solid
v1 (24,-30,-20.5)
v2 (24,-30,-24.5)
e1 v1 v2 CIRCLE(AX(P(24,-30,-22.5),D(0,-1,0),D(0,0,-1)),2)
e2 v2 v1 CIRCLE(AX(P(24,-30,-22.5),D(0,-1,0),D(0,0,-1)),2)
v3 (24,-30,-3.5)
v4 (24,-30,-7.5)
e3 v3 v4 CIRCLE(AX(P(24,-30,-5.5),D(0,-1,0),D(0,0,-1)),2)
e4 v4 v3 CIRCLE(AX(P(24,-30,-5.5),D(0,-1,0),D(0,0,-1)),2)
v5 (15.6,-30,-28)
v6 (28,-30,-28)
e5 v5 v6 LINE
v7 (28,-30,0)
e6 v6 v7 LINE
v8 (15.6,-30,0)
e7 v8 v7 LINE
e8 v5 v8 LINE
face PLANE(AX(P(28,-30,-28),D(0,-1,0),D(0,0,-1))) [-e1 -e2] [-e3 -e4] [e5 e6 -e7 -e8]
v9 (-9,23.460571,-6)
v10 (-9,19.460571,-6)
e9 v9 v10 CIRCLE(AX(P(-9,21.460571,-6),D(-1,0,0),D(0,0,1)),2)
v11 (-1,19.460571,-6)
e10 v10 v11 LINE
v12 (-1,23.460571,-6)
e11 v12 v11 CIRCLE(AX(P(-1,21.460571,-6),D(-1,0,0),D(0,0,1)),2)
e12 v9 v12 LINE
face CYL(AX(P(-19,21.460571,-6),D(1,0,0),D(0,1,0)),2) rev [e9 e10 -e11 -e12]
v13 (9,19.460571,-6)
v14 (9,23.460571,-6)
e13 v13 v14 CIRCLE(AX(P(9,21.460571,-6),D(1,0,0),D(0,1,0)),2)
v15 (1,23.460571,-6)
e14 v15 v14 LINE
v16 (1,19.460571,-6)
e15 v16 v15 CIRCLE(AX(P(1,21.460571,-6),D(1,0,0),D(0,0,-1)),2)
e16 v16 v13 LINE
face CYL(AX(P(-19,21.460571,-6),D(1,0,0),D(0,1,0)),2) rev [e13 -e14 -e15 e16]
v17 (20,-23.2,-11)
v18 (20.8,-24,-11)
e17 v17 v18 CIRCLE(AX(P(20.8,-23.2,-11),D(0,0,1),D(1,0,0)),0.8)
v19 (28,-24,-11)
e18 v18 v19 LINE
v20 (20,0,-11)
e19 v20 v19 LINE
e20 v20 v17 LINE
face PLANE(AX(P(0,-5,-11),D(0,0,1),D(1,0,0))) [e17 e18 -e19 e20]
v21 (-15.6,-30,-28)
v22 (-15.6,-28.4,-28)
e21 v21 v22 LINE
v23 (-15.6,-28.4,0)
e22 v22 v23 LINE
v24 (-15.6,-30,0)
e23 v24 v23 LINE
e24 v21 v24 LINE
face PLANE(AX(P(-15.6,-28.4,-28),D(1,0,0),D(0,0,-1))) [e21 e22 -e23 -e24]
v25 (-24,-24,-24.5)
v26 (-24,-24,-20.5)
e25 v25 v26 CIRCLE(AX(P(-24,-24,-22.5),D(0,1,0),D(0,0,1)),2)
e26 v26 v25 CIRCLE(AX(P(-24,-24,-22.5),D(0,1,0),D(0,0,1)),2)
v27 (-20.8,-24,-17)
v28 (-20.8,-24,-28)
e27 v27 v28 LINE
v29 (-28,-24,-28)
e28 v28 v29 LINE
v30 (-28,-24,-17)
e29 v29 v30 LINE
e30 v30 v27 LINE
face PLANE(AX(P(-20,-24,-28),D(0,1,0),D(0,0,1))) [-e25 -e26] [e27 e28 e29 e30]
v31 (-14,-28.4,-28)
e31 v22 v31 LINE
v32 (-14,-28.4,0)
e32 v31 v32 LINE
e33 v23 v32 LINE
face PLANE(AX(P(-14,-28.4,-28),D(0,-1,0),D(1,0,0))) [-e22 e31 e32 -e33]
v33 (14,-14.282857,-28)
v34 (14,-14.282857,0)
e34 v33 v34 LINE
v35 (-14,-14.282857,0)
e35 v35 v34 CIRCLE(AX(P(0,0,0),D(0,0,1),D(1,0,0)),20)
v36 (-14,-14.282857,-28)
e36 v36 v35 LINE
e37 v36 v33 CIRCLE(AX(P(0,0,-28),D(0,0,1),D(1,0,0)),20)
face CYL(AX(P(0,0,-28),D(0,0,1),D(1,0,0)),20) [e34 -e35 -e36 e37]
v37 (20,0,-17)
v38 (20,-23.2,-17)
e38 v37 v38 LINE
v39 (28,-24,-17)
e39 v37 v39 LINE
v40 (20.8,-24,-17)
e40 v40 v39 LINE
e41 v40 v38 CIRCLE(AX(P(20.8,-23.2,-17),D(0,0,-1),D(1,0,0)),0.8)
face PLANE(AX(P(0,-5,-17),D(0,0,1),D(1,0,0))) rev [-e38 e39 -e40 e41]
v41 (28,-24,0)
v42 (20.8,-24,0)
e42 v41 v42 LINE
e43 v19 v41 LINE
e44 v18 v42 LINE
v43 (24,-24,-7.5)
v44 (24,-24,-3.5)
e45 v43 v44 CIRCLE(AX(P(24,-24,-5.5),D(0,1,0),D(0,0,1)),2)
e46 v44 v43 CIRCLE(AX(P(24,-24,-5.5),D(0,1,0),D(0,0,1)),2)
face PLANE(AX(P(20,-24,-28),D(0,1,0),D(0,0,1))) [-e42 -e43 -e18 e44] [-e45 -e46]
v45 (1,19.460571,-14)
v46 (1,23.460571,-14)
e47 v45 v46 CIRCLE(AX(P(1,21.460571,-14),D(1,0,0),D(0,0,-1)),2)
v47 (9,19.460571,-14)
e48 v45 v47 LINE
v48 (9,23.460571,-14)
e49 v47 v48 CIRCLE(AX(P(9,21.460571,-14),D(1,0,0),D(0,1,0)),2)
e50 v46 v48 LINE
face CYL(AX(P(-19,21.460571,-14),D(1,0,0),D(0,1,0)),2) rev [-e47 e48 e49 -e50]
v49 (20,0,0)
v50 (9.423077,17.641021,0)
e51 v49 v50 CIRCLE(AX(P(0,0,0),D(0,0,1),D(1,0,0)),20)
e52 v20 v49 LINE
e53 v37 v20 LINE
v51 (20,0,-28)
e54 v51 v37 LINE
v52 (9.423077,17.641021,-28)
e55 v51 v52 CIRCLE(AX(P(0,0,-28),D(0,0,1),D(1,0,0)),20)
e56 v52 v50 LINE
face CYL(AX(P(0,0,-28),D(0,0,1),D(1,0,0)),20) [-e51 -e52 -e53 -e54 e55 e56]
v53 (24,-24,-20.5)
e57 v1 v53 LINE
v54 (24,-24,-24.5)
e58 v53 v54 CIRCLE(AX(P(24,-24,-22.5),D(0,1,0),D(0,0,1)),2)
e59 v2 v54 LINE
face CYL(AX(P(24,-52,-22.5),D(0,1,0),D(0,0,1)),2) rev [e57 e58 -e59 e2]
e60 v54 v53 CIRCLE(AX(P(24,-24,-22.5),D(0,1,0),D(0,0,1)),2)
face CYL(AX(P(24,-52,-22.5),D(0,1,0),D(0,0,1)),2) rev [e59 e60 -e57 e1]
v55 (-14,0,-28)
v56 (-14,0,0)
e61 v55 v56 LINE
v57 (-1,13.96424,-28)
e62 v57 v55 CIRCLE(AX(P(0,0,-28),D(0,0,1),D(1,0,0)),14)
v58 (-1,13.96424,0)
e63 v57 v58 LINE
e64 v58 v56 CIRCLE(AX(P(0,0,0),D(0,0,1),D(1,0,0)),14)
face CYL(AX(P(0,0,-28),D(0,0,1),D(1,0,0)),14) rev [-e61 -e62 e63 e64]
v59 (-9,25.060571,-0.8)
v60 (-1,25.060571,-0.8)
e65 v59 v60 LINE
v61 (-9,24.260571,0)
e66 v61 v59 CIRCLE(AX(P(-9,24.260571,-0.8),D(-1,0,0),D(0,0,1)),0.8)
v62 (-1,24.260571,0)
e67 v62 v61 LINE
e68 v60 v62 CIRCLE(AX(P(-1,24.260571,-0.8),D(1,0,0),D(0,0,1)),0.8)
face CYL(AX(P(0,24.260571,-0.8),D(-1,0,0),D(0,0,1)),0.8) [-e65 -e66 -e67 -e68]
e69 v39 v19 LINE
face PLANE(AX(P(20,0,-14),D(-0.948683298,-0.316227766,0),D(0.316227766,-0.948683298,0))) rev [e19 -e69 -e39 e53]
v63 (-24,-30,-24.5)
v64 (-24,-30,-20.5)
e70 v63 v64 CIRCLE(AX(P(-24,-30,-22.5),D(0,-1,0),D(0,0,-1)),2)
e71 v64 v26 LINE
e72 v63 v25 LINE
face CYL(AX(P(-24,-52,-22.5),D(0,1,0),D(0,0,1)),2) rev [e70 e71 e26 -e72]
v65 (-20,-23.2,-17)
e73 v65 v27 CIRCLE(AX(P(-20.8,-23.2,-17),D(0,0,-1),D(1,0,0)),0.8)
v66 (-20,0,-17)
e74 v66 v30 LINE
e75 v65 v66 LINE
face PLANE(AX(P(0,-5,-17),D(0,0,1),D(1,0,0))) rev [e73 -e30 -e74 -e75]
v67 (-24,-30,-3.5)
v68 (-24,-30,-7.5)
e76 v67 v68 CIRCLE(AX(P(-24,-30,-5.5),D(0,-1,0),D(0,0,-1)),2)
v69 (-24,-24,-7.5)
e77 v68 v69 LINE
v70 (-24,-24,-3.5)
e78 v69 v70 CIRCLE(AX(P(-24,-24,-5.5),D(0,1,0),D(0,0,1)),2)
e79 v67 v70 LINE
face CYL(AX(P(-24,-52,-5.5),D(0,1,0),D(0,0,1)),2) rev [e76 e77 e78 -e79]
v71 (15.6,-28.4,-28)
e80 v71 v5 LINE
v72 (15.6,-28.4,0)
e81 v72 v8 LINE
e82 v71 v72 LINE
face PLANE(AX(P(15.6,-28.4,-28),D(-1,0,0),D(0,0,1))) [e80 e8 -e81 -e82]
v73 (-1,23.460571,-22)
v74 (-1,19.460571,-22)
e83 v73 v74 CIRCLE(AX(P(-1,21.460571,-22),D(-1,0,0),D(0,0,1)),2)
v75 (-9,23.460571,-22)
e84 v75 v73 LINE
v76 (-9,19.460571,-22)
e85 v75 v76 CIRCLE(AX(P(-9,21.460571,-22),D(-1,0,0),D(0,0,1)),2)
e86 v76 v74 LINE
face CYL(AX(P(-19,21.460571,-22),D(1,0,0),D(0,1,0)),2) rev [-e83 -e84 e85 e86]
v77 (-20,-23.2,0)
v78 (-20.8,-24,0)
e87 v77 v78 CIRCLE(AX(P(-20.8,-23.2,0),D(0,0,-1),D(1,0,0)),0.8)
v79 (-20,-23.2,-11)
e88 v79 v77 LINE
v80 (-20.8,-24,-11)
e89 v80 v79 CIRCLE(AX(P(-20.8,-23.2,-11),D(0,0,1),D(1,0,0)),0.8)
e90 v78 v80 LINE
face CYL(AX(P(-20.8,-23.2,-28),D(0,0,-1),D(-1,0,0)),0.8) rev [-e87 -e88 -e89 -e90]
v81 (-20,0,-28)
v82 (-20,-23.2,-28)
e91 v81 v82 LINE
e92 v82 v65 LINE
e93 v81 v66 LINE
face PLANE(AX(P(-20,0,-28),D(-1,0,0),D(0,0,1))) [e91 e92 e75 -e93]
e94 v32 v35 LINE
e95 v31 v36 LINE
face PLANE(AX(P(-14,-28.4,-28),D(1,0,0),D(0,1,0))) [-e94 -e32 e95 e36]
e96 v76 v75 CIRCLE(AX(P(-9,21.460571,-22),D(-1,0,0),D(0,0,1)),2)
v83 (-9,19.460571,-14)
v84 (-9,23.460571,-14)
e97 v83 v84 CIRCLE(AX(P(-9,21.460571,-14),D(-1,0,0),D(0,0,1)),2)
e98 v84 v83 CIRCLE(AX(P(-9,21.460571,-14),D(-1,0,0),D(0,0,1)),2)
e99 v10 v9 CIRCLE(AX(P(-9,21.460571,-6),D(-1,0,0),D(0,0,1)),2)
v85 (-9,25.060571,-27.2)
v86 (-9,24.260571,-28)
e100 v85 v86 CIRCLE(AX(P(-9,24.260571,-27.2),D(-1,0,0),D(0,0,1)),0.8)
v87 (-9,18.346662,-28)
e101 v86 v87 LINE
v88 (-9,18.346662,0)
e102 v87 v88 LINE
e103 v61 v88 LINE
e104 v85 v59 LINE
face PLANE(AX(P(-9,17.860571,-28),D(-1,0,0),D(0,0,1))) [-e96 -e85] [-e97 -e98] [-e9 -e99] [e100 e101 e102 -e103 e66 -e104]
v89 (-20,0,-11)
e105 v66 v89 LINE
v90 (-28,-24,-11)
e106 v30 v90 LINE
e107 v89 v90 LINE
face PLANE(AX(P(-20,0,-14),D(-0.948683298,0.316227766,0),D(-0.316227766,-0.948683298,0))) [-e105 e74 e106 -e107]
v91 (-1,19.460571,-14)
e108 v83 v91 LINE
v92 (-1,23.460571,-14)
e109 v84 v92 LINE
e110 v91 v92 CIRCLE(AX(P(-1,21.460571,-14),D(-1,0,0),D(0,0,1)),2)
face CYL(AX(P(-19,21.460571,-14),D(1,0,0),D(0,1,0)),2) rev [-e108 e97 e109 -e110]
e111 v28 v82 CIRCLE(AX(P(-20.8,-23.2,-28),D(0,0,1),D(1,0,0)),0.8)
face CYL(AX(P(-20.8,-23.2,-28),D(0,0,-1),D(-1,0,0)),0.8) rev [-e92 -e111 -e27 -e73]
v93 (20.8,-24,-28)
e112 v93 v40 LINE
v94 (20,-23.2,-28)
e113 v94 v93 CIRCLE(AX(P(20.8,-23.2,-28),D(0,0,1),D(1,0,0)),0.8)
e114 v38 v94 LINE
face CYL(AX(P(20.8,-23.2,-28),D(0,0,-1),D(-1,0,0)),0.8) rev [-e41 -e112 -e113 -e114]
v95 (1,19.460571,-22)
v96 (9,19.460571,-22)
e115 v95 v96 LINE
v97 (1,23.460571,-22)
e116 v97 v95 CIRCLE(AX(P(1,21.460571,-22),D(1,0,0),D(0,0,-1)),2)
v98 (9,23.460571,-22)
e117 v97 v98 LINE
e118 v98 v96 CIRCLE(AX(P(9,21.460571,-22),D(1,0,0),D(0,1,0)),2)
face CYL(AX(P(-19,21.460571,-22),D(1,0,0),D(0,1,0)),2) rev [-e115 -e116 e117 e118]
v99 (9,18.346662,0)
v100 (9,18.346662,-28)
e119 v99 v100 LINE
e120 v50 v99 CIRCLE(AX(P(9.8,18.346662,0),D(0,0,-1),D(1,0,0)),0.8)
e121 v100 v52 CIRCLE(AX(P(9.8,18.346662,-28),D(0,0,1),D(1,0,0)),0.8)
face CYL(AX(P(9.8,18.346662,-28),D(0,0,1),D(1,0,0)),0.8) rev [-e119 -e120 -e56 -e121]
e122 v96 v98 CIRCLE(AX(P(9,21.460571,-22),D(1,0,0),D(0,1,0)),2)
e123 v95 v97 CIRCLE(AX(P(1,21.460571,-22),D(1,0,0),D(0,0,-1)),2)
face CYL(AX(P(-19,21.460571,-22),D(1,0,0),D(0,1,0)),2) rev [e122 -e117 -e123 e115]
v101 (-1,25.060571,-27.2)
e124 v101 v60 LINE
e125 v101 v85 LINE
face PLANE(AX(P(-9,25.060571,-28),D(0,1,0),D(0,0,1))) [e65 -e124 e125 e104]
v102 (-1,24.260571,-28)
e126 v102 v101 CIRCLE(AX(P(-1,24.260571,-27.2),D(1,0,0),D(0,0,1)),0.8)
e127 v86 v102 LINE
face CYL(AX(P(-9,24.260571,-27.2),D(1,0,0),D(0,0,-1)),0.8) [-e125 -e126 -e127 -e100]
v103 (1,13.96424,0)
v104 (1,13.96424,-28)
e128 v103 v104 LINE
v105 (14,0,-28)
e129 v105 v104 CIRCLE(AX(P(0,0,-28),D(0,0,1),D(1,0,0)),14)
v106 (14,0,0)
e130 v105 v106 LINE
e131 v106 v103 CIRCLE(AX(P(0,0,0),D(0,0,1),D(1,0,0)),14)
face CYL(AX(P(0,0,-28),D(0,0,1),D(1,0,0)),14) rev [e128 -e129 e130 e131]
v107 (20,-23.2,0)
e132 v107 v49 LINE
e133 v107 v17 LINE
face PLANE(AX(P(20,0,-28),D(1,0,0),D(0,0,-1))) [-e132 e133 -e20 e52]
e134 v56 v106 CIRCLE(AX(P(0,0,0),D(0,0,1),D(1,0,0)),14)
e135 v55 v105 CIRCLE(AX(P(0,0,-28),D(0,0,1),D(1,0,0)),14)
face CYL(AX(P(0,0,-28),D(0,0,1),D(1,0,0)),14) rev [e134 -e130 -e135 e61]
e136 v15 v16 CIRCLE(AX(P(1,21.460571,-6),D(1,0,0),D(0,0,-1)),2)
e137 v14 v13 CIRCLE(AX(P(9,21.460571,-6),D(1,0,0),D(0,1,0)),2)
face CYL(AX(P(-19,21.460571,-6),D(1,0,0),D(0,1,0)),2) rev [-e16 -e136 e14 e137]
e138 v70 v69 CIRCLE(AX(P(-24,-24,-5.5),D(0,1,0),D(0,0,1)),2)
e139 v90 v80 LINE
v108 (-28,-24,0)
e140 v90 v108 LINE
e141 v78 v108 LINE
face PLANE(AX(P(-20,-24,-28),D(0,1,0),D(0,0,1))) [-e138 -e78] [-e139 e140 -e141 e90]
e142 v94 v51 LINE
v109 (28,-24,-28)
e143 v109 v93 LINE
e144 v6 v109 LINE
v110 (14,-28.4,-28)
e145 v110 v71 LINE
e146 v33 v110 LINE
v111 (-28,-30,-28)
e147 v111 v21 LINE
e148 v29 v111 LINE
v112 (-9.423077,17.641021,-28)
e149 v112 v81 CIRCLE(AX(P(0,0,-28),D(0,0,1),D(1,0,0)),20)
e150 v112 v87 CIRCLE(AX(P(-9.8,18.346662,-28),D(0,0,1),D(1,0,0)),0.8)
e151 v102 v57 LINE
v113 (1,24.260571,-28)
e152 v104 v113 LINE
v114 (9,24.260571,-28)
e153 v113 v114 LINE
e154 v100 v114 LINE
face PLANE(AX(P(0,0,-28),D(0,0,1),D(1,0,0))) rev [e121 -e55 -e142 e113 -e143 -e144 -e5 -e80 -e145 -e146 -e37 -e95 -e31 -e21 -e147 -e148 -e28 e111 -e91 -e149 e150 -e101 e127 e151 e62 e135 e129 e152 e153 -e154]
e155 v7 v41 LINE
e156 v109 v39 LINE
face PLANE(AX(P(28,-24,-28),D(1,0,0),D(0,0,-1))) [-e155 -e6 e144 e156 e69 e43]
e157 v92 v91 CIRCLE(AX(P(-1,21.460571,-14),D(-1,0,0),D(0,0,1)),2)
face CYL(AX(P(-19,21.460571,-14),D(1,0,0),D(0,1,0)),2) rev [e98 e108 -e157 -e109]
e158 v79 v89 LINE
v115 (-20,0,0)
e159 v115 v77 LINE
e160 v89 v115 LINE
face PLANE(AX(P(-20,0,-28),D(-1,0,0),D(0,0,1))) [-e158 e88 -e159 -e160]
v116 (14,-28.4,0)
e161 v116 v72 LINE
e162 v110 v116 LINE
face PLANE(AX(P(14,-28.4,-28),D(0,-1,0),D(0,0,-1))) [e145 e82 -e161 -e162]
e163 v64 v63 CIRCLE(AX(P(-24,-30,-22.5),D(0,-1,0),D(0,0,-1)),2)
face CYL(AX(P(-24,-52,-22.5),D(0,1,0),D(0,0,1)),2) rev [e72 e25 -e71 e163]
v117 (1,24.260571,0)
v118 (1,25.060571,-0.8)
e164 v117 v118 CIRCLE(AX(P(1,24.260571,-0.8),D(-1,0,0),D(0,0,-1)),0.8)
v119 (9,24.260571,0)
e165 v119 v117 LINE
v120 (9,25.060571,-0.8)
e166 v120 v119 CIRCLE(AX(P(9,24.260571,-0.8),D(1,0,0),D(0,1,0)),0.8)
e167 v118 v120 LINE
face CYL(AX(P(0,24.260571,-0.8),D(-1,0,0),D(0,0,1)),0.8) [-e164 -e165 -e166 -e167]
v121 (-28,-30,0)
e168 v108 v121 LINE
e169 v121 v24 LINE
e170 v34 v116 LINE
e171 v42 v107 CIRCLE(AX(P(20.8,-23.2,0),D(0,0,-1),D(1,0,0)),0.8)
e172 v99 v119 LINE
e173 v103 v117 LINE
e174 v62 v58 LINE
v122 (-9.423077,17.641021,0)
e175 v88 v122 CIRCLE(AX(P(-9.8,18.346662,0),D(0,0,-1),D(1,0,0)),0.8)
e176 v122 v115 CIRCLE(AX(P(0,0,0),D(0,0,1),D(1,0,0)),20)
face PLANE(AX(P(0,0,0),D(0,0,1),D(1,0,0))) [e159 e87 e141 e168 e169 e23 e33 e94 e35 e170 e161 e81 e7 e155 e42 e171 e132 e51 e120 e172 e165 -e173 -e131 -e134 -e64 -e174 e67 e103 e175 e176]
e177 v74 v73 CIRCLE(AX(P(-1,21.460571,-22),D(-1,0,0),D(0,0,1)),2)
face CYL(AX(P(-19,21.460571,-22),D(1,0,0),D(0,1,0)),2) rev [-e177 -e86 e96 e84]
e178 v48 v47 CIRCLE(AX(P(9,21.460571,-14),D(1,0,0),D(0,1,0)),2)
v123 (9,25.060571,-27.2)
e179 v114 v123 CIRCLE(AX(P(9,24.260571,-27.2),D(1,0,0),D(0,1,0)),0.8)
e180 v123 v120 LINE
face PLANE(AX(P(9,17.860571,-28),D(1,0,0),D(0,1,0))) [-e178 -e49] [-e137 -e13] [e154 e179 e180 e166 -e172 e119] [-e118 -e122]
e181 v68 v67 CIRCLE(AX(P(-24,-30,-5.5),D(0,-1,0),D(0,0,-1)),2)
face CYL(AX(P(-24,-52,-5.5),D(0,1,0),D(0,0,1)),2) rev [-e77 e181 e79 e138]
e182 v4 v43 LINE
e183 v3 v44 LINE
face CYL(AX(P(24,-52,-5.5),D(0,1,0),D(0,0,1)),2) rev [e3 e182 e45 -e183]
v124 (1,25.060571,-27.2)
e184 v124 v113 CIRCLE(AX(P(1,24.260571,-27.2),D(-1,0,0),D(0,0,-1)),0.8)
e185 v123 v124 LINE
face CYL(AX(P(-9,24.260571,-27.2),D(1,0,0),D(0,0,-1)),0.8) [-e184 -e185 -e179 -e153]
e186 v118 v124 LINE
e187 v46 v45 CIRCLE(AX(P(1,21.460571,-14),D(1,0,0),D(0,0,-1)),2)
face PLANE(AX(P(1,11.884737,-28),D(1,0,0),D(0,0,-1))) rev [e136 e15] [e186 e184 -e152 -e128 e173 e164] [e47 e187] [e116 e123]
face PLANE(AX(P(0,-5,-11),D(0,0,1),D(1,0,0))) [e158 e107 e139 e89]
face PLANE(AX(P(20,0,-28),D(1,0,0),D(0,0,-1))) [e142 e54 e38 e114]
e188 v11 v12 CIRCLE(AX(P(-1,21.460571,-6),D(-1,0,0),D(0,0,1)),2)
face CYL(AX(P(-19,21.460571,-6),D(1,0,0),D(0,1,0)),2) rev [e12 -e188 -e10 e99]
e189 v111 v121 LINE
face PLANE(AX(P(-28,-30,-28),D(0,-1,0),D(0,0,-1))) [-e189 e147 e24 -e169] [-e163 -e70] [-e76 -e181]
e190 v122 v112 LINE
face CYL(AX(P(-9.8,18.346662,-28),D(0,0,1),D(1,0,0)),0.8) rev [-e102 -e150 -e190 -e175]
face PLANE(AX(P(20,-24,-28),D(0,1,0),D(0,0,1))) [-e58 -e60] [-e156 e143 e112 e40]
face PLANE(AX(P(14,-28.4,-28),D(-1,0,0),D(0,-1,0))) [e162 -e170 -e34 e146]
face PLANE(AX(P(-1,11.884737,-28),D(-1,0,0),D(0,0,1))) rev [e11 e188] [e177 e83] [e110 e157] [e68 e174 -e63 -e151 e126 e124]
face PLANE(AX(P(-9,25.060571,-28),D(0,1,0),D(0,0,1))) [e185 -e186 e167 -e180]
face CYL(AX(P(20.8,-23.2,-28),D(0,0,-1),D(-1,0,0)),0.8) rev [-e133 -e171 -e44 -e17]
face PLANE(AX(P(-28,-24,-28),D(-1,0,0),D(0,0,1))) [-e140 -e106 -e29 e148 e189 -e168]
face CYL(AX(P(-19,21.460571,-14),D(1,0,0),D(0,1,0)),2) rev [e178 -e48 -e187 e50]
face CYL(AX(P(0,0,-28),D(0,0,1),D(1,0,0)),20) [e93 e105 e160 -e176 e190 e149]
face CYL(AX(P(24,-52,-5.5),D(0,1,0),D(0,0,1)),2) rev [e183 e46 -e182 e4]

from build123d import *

# Parameters (mm, degrees)
OMEGA_PROFILE_SKETCH_R         = 14
OMEGA_BODY_DEPTH               = 28
SUPPORT_RIB_REACH              = 45.359
SUPPORT_RIB_SKETCH_WALL_W      = 114.016154836
SUPPORT_RIB_SKETCH_WALL_H      = 6
BASE_MOUNTING_HOLES_SKETCH_R   = 2
BASE_MOUNTING_HOLES_DEPTH      = 28
CLAMP_LUG_DEPTH                = 28
SPLIT_SLOT_SKETCH_W            = 2
SPLIT_SLOT_SKETCH_H            = 18.147677211
SPLIT_SLOT_2MM_DEPTH           = 28
CLAMP_SCREW_HOLES_SKETCH_R     = 2
CLAMP_SCREW_HOLES_3X_3_6_DEPTH = 28
EDGE_FILLETS_R0_8_R            = 0.8


with BuildPart() as part:
    # Omega Profile Sketch → Omega Body (new body)
    with BuildSketch(Plane.XY):
        with BuildLine():
            Line((-20, 0), (-20, -24))
            Line((-20, -24), (-28, -24))
            Line((-28, -24), (-28, -30))
            Line((-28, -30), (-15.6, -30))
            Line((-15.6, -30), (-15.6, -28.4))
            Line((-15.6, -28.4), (-14, -28.4))
            Line((-14, -28.4), (-14, -14.282856857))
            ThreePointArc((-14, -14.282856857), (0, -20), (14, -14.282856857))
            Line((14, -14.282856857), (14, -28.4))
            Line((14, -28.4), (15.6, -28.4))
            Line((15.6, -28.4), (15.6, -30))
            Line((15.6, -30), (28, -30))
            Line((28, -30), (28, -24))
            Line((28, -24), (20, -24))
            Line((20, -24), (20, 0))
            ThreePointArc((20, 0), (0, 20), (-20, 0))
        make_face()
        Circle(OMEGA_PROFILE_SKETCH_R, mode=Mode.SUBTRACT)
    extrude(amount=-OMEGA_BODY_DEPTH)

    # Support Rib Sketch wall → Support Rib (add, up to next)
    with BuildSketch(Plane(origin=(24, -12, -14), x_dir=(0.316227766017, -0.948683298051, 0), z_dir=(0.948683298051, 0.316227766017, 0)), mode=Mode.PRIVATE) as support_rib_sk1:
        Rectangle(SUPPORT_RIB_SKETCH_WALL_W, SUPPORT_RIB_SKETCH_WALL_H)
    support_rib_tool1 = extrude(support_rib_sk1.sketch, amount=-SUPPORT_RIB_REACH, mode=Mode.PRIVATE) - part.part
    support_rib = support_rib_tool1.solids().sort_by_distance((24, -12, -14))[0]
    add(support_rib)

    # Support Rib Mirror: Support Rib across plane
    add(support_rib.mirror(Plane(origin=(0, 0, 0), x_dir=(0, 0, 1), z_dir=(1, 0, 0))))

    # Base Mounting Holes Sketch → Base Mounting Holes (cut)
    with BuildSketch(Plane(origin=(0, -24, 0), x_dir=(1, 0, 0), z_dir=(0, 1, 0))):
        with Locations(Location((24, 22.5, 0), (0, 0, 270))):
            Circle(BASE_MOUNTING_HOLES_SKETCH_R)
        with Locations(Location((24, 5.5, 0), (0, 0, 270))):
            Circle(BASE_MOUNTING_HOLES_SKETCH_R)
        with Locations(Location((-24, 5.5, 0), (0, 0, 270))):
            Circle(BASE_MOUNTING_HOLES_SKETCH_R)
        with Locations(Location((-24, 22.5, 0), (0, 0, 270))):
            Circle(BASE_MOUNTING_HOLES_SKETCH_R)
    extrude(amount=-BASE_MOUNTING_HOLES_DEPTH, mode=Mode.SUBTRACT)

    # Clamp Lug Sketch → Clamp Lug (add)
    with BuildSketch(Plane.XY):
        with BuildLine():
            Line((-9, 17.860571099), (-9, 25.060571099))
            Line((-9, 25.060571099), (9, 25.060571099))
            Line((9, 25.060571099), (9, 17.860571099))
            ThreePointArc((9, 17.860571099), (0, 20), (-9, 17.860571099))
        make_face()
    extrude(amount=-CLAMP_LUG_DEPTH)

    # Split Slot Sketch → Split Slot 2mm (cut)
    with BuildSketch(Plane.XY):
        with Locations((0, 20.958575759)):
            Rectangle(SPLIT_SLOT_SKETCH_W, SPLIT_SLOT_SKETCH_H)
    extrude(amount=-SPLIT_SLOT_2MM_DEPTH, mode=Mode.SUBTRACT)

    # Clamp Screw Holes Sketch → Clamp Screw Holes 3xØ3.6 (cut)
    with BuildSketch(Plane(origin=(9, 0, 0), x_dir=(0, 0, -1), z_dir=(1, 0, 0))):
        with Locations(Location((6, 21.460571099, 0), (0, 0, 180))):
            Circle(CLAMP_SCREW_HOLES_SKETCH_R)
        with Locations(Location((14, 21.460571099, 0), (0, 0, 180))):
            Circle(CLAMP_SCREW_HOLES_SKETCH_R)
        with Locations(Location((22, 21.460571099, 0), (0, 0, 180))):
            Circle(CLAMP_SCREW_HOLES_SKETCH_R)
    extrude(amount=-CLAMP_SCREW_HOLES_3X_3_6_DEPTH, mode=Mode.SUBTRACT)

    # Edge Fillets R0.8
    edge_fillets_r0_8_edges = [part.edges().sort_by_distance(p)[0] for p in [
        (-20, -24, -5.5),
        (9, 17.860571099, -14),
        (-9, 17.860571099, -14),
        (5, 25.060571099, -28),
        (5, 25.060571099, 0),
        (-5, 25.060571099, 0),
        (-5, 25.060571099, -28),
        (20, -24, -22.5),
        (-20, -24, -22.5),
        (20, -24, -5.5),
    ]]
    fillet(edge_fillets_r0_8_edges, radius=EDGE_FILLETS_R0_8_R)


solid = part.part
